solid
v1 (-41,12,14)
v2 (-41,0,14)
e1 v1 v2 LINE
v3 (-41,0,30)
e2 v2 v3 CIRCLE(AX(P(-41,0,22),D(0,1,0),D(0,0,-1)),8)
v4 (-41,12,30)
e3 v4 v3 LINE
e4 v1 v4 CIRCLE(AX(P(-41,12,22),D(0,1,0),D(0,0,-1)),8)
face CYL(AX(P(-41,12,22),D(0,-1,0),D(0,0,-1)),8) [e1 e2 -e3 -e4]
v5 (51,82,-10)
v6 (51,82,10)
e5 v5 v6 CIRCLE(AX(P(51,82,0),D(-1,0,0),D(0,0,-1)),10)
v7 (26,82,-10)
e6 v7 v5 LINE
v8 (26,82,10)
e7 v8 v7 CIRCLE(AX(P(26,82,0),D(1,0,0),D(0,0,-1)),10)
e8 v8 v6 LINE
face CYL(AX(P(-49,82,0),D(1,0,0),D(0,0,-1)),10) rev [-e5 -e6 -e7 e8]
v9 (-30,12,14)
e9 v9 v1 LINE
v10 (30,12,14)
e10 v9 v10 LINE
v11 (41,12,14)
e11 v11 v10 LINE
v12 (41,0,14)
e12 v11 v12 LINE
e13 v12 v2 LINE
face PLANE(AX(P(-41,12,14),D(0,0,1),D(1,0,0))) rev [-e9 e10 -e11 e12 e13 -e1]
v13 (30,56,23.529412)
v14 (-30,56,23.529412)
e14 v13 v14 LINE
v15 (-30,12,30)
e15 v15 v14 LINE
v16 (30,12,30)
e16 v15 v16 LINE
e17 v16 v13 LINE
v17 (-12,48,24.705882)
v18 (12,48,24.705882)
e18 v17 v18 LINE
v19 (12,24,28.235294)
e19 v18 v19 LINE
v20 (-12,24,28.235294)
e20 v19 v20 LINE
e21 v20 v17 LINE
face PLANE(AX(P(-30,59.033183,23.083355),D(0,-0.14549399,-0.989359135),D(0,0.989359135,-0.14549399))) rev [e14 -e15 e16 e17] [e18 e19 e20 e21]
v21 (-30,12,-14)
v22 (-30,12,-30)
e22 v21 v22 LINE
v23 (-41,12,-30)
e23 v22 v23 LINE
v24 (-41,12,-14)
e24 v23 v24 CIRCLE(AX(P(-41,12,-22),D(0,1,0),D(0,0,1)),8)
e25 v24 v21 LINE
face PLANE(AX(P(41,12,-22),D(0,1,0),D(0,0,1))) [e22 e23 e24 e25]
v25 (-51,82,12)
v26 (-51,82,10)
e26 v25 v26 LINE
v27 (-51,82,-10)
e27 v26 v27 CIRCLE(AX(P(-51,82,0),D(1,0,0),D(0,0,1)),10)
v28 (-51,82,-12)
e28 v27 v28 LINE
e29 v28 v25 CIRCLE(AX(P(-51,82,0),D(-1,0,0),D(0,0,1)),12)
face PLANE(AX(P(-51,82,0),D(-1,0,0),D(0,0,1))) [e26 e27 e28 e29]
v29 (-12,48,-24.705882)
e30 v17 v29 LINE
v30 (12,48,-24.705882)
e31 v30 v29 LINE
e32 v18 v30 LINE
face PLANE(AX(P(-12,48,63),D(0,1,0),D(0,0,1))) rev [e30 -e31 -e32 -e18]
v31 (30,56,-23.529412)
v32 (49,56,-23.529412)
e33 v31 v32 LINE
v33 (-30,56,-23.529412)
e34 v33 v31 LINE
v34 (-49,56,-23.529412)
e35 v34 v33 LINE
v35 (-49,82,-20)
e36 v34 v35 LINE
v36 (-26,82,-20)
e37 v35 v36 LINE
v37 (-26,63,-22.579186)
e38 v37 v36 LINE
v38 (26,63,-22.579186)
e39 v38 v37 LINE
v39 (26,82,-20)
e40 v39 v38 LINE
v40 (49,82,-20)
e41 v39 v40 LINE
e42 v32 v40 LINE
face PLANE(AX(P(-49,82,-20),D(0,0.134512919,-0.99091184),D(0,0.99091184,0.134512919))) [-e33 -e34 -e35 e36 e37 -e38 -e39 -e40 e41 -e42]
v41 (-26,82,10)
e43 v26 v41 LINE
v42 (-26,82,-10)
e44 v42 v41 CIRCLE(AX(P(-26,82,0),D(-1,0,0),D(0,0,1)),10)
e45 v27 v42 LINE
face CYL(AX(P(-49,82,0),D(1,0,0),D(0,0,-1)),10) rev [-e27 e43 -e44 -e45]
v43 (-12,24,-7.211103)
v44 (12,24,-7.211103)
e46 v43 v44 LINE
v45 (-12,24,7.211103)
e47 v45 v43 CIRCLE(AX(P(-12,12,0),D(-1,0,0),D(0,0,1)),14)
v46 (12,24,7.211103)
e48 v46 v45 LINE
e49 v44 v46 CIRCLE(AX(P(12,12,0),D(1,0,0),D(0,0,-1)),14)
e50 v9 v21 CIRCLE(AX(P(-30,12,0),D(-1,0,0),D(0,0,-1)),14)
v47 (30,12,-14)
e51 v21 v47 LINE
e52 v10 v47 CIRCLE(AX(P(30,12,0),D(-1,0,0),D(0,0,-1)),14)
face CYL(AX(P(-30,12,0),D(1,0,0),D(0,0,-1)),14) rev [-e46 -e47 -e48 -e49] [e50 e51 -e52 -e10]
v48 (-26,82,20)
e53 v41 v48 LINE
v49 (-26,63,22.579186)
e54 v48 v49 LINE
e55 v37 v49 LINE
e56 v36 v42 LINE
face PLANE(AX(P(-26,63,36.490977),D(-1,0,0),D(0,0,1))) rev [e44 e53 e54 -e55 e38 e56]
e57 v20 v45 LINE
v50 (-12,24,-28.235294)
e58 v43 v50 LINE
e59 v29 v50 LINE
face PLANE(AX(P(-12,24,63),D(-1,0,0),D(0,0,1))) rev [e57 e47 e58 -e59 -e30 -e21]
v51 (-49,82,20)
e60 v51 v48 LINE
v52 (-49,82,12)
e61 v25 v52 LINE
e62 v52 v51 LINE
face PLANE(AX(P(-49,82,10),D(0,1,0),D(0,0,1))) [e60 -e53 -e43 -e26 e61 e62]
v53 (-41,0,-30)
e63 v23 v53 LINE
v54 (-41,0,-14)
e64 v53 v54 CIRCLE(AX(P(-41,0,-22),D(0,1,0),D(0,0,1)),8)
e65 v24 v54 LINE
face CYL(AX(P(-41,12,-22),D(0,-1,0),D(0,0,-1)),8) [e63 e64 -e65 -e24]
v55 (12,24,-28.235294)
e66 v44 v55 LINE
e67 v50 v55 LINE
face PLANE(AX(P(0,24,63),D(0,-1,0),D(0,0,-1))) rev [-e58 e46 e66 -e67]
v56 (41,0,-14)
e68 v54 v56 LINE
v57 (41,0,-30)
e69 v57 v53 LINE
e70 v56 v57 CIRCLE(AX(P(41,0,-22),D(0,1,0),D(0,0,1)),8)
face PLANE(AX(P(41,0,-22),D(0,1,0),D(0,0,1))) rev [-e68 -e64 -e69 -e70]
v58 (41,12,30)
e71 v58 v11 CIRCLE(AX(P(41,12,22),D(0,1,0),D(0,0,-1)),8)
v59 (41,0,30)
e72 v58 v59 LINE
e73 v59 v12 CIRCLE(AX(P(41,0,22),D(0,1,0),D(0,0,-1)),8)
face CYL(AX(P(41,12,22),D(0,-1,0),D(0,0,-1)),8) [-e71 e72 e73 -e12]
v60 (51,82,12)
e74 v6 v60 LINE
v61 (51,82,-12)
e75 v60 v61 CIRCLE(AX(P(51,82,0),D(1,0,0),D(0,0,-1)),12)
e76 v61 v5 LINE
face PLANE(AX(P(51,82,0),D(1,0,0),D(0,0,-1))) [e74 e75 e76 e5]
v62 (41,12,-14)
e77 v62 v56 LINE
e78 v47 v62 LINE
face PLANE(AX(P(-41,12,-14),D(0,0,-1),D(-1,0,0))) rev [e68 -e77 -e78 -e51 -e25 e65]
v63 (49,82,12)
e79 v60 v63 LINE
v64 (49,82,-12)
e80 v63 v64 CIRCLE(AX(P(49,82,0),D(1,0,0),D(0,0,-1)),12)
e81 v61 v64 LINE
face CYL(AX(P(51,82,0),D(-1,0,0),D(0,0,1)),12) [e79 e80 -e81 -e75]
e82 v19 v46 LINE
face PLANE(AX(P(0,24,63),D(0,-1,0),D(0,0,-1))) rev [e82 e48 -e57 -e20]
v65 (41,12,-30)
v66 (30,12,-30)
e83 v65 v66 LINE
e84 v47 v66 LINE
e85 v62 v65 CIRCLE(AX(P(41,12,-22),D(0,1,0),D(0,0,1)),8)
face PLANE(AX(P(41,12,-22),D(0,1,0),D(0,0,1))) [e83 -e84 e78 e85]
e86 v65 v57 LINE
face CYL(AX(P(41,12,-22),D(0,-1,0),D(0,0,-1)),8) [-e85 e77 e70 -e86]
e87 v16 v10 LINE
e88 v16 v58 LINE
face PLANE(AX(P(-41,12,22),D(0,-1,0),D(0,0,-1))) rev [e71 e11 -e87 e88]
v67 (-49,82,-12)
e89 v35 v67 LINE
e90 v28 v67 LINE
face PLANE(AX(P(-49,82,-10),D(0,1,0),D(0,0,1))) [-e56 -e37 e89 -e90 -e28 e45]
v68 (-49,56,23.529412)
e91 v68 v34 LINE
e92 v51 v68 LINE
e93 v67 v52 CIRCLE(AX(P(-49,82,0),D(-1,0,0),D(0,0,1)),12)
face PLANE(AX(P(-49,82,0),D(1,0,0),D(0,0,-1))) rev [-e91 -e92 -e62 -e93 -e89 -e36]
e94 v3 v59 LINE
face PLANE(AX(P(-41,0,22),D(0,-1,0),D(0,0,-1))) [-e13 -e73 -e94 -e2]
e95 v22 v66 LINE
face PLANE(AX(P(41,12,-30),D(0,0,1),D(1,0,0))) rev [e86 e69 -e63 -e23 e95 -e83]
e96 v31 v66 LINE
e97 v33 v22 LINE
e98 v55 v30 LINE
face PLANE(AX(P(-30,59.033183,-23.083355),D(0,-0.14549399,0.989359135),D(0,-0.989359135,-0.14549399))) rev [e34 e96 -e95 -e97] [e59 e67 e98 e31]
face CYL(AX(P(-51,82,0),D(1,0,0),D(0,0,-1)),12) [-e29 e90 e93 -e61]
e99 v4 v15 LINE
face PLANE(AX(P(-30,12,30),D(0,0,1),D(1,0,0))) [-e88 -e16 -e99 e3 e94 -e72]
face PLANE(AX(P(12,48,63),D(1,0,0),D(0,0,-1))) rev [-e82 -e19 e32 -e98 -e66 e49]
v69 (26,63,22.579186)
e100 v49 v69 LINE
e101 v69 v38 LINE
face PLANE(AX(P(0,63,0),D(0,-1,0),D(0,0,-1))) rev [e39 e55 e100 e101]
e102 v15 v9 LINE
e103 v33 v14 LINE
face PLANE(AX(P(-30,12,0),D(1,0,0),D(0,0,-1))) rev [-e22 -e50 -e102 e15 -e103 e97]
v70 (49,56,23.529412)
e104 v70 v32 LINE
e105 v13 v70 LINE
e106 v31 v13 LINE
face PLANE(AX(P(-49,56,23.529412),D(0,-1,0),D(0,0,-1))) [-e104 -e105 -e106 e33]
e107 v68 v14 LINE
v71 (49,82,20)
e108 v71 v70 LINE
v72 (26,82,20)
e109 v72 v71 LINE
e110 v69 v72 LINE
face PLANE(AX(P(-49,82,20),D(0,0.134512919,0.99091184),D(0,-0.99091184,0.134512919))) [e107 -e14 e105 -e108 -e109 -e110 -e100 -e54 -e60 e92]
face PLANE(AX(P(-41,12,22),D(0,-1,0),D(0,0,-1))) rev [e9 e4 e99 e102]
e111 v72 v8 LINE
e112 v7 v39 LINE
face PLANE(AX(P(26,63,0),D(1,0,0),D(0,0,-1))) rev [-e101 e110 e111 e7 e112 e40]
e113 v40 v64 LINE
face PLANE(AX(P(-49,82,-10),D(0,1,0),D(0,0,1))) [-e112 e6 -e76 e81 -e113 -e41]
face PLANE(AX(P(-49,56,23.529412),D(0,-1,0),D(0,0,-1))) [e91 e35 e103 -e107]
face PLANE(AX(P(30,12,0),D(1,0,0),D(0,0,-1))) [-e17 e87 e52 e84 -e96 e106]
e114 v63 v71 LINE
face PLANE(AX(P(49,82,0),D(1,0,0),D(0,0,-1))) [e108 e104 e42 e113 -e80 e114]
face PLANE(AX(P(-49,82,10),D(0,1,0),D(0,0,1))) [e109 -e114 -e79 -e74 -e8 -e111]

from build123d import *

# Parameters (mm, degrees)
BASE_BODY_DEPTH         = 12
BASE_BODY_2_DEPTH       = 12
FOOT_BOSS_60_DEPTH      = 60
WINDOW_CUT_DEPTH        = 60
SADDLE_ENDS_98_DEPTH    = 98
SADDLE_CRADLE_CUT_DEPTH = 19
ARCH_RELIEF_CUT_DEPTH   = 93
RETAINING_START         = 2
RETAINING_LIP_A_DEPTH   = 2
RETAINING_LIP_B_DEPTH   = 2


with BuildPart() as part:
    # Base Body Sketch → Base Body (new body)
    with BuildSketch(Plane(origin=(0, 0, 0), x_dir=(1, 0, 0), z_dir=(0, 1, 0))):
        with BuildLine():
            Line((-41, -14), (41, -14))
            ThreePointArc((41, -14), (49, -22), (41, -30))
            Line((41, -30), (-41, -30))
            ThreePointArc((-41, -30), (-49, -22), (-41, -14))
        make_face()
    extrude(amount=BASE_BODY_DEPTH)



with BuildPart() as body_2:
    # Base Body Sketch → Base Body 2 (new body)
    with BuildSketch(Plane(origin=(0, 0, 0), x_dir=(1, 0, 0), z_dir=(0, 1, 0))):
        with BuildLine():
            Line((41, 30), (-41, 30))
            ThreePointArc((-41, 30), (-49, 22), (-41, 14))
            Line((-41, 14), (41, 14))
            ThreePointArc((41, 14), (49, 22), (41, 30))
        make_face()
    extrude(amount=BASE_BODY_2_DEPTH)


with BuildPart() as part_1:
    add(part.part)

    add(body_2.part)  # Foot Boss 60 merges body 2
    # Foot Boss Sketch → Foot Boss 60 (add)
    with BuildSketch(Plane(origin=(30, 0, 0), x_dir=(0, 0, -1), z_dir=(1, 0, 0))):
        with BuildLine():
            Line((-14, 12), (-30, 12))
            Line((-30, 12), (-30, 56))
            Line((-30, 56), (30, 56))
            Line((30, 56), (30, 12))
            Line((30, 12), (14, 12))
            ThreePointArc((14, 12), (0, 26), (-14, 12))
        make_face()
    extrude(amount=-FOOT_BOSS_60_DEPTH)

    # Window Cut Sketch → Window Cut (cut)
    with BuildSketch(Plane(origin=(30, 0, 0), x_dir=(0, 0, -1), z_dir=(1, 0, 0))):
        Polygon((-23.08335547, 59.033182801), (-30, 12), (-33.835274918, 12), (-33.835274918, 59.033182801), align=None)
        Polygon((23.08335547, 59.033182801), (30, 12), (40.995792327, 12), (40.995792327, 59.033182801), align=None)
    extrude(amount=-WINDOW_CUT_DEPTH, mode=Mode.SUBTRACT)

    # Saddle Ends Sketch → Saddle Ends 98 (add)
    with BuildSketch(Plane(origin=(49, 0, 0), x_dir=(0, 0, -1), z_dir=(1, 0, 0))):
        with BuildLine():
            Line((10, 82), (20, 82))
            Line((20, 82), (23.529411765, 56))
            Line((23.529411765, 56), (-23.529411765, 56))
            Line((-23.529411765, 56), (-20, 82))
            Line((-20, 82), (-10, 82))
            ThreePointArc((-10, 82), (0, 72), (10, 82))
        make_face()
    extrude(amount=-SADDLE_ENDS_98_DEPTH)

    # Saddle Cradle Cut Sketch → Saddle Cradle Cut (cut)
    with BuildSketch(Plane(origin=(0, 82, 0), x_dir=(1, 0, 0), z_dir=(0, 1, 0))):
        Polygon((26, 0), (26, -36.490977082), (-26, -36.490977082), (-26, 35.721826881), (26, 35.721826881), align=None)
    extrude(amount=-SADDLE_CRADLE_CUT_DEPTH, mode=Mode.SUBTRACT)

    # Arch Relief Cut Sketch → Arch Relief Cut (cut)
    with BuildSketch(Plane(origin=(0, 0, -30), x_dir=(-1, 0, 0), z_dir=(0, 0, -1))):
        Polygon((0, 24), (12, 24), (12, 48), (-12, 48), (-12, 24), align=None)
    extrude(amount=-ARCH_RELIEF_CUT_DEPTH, mode=Mode.SUBTRACT)

    # Retaining Lip A Sketch → Retaining Lip A (add)
    with BuildSketch(Plane(origin=(49, 0, 0), x_dir=(0, 0, -1), z_dir=(1, 0, 0)).offset(RETAINING_START)):
        with BuildLine():
            Line((-12, 82), (-10, 82))
            ThreePointArc((-10, 82), (0, 72), (10, 82))
            Line((10, 82), (12, 82))
            ThreePointArc((12, 82), (0, 70), (-12, 82))
        make_face()
    extrude(amount=-RETAINING_LIP_A_DEPTH)

    # Retaining Lip B Sketch → Retaining Lip B (add)
    with BuildSketch(Plane.ZY.offset(49)):
        with BuildLine():
            Line((10, 82), (12, 82))
            ThreePointArc((12, 82), (0, 70), (-12, 82))
            Line((-12, 82), (-10, 82))
            ThreePointArc((-10, 82), (0, 72), (10, 82))
        make_face()
    extrude(amount=RETAINING_LIP_B_DEPTH)


solid = part_1.part
